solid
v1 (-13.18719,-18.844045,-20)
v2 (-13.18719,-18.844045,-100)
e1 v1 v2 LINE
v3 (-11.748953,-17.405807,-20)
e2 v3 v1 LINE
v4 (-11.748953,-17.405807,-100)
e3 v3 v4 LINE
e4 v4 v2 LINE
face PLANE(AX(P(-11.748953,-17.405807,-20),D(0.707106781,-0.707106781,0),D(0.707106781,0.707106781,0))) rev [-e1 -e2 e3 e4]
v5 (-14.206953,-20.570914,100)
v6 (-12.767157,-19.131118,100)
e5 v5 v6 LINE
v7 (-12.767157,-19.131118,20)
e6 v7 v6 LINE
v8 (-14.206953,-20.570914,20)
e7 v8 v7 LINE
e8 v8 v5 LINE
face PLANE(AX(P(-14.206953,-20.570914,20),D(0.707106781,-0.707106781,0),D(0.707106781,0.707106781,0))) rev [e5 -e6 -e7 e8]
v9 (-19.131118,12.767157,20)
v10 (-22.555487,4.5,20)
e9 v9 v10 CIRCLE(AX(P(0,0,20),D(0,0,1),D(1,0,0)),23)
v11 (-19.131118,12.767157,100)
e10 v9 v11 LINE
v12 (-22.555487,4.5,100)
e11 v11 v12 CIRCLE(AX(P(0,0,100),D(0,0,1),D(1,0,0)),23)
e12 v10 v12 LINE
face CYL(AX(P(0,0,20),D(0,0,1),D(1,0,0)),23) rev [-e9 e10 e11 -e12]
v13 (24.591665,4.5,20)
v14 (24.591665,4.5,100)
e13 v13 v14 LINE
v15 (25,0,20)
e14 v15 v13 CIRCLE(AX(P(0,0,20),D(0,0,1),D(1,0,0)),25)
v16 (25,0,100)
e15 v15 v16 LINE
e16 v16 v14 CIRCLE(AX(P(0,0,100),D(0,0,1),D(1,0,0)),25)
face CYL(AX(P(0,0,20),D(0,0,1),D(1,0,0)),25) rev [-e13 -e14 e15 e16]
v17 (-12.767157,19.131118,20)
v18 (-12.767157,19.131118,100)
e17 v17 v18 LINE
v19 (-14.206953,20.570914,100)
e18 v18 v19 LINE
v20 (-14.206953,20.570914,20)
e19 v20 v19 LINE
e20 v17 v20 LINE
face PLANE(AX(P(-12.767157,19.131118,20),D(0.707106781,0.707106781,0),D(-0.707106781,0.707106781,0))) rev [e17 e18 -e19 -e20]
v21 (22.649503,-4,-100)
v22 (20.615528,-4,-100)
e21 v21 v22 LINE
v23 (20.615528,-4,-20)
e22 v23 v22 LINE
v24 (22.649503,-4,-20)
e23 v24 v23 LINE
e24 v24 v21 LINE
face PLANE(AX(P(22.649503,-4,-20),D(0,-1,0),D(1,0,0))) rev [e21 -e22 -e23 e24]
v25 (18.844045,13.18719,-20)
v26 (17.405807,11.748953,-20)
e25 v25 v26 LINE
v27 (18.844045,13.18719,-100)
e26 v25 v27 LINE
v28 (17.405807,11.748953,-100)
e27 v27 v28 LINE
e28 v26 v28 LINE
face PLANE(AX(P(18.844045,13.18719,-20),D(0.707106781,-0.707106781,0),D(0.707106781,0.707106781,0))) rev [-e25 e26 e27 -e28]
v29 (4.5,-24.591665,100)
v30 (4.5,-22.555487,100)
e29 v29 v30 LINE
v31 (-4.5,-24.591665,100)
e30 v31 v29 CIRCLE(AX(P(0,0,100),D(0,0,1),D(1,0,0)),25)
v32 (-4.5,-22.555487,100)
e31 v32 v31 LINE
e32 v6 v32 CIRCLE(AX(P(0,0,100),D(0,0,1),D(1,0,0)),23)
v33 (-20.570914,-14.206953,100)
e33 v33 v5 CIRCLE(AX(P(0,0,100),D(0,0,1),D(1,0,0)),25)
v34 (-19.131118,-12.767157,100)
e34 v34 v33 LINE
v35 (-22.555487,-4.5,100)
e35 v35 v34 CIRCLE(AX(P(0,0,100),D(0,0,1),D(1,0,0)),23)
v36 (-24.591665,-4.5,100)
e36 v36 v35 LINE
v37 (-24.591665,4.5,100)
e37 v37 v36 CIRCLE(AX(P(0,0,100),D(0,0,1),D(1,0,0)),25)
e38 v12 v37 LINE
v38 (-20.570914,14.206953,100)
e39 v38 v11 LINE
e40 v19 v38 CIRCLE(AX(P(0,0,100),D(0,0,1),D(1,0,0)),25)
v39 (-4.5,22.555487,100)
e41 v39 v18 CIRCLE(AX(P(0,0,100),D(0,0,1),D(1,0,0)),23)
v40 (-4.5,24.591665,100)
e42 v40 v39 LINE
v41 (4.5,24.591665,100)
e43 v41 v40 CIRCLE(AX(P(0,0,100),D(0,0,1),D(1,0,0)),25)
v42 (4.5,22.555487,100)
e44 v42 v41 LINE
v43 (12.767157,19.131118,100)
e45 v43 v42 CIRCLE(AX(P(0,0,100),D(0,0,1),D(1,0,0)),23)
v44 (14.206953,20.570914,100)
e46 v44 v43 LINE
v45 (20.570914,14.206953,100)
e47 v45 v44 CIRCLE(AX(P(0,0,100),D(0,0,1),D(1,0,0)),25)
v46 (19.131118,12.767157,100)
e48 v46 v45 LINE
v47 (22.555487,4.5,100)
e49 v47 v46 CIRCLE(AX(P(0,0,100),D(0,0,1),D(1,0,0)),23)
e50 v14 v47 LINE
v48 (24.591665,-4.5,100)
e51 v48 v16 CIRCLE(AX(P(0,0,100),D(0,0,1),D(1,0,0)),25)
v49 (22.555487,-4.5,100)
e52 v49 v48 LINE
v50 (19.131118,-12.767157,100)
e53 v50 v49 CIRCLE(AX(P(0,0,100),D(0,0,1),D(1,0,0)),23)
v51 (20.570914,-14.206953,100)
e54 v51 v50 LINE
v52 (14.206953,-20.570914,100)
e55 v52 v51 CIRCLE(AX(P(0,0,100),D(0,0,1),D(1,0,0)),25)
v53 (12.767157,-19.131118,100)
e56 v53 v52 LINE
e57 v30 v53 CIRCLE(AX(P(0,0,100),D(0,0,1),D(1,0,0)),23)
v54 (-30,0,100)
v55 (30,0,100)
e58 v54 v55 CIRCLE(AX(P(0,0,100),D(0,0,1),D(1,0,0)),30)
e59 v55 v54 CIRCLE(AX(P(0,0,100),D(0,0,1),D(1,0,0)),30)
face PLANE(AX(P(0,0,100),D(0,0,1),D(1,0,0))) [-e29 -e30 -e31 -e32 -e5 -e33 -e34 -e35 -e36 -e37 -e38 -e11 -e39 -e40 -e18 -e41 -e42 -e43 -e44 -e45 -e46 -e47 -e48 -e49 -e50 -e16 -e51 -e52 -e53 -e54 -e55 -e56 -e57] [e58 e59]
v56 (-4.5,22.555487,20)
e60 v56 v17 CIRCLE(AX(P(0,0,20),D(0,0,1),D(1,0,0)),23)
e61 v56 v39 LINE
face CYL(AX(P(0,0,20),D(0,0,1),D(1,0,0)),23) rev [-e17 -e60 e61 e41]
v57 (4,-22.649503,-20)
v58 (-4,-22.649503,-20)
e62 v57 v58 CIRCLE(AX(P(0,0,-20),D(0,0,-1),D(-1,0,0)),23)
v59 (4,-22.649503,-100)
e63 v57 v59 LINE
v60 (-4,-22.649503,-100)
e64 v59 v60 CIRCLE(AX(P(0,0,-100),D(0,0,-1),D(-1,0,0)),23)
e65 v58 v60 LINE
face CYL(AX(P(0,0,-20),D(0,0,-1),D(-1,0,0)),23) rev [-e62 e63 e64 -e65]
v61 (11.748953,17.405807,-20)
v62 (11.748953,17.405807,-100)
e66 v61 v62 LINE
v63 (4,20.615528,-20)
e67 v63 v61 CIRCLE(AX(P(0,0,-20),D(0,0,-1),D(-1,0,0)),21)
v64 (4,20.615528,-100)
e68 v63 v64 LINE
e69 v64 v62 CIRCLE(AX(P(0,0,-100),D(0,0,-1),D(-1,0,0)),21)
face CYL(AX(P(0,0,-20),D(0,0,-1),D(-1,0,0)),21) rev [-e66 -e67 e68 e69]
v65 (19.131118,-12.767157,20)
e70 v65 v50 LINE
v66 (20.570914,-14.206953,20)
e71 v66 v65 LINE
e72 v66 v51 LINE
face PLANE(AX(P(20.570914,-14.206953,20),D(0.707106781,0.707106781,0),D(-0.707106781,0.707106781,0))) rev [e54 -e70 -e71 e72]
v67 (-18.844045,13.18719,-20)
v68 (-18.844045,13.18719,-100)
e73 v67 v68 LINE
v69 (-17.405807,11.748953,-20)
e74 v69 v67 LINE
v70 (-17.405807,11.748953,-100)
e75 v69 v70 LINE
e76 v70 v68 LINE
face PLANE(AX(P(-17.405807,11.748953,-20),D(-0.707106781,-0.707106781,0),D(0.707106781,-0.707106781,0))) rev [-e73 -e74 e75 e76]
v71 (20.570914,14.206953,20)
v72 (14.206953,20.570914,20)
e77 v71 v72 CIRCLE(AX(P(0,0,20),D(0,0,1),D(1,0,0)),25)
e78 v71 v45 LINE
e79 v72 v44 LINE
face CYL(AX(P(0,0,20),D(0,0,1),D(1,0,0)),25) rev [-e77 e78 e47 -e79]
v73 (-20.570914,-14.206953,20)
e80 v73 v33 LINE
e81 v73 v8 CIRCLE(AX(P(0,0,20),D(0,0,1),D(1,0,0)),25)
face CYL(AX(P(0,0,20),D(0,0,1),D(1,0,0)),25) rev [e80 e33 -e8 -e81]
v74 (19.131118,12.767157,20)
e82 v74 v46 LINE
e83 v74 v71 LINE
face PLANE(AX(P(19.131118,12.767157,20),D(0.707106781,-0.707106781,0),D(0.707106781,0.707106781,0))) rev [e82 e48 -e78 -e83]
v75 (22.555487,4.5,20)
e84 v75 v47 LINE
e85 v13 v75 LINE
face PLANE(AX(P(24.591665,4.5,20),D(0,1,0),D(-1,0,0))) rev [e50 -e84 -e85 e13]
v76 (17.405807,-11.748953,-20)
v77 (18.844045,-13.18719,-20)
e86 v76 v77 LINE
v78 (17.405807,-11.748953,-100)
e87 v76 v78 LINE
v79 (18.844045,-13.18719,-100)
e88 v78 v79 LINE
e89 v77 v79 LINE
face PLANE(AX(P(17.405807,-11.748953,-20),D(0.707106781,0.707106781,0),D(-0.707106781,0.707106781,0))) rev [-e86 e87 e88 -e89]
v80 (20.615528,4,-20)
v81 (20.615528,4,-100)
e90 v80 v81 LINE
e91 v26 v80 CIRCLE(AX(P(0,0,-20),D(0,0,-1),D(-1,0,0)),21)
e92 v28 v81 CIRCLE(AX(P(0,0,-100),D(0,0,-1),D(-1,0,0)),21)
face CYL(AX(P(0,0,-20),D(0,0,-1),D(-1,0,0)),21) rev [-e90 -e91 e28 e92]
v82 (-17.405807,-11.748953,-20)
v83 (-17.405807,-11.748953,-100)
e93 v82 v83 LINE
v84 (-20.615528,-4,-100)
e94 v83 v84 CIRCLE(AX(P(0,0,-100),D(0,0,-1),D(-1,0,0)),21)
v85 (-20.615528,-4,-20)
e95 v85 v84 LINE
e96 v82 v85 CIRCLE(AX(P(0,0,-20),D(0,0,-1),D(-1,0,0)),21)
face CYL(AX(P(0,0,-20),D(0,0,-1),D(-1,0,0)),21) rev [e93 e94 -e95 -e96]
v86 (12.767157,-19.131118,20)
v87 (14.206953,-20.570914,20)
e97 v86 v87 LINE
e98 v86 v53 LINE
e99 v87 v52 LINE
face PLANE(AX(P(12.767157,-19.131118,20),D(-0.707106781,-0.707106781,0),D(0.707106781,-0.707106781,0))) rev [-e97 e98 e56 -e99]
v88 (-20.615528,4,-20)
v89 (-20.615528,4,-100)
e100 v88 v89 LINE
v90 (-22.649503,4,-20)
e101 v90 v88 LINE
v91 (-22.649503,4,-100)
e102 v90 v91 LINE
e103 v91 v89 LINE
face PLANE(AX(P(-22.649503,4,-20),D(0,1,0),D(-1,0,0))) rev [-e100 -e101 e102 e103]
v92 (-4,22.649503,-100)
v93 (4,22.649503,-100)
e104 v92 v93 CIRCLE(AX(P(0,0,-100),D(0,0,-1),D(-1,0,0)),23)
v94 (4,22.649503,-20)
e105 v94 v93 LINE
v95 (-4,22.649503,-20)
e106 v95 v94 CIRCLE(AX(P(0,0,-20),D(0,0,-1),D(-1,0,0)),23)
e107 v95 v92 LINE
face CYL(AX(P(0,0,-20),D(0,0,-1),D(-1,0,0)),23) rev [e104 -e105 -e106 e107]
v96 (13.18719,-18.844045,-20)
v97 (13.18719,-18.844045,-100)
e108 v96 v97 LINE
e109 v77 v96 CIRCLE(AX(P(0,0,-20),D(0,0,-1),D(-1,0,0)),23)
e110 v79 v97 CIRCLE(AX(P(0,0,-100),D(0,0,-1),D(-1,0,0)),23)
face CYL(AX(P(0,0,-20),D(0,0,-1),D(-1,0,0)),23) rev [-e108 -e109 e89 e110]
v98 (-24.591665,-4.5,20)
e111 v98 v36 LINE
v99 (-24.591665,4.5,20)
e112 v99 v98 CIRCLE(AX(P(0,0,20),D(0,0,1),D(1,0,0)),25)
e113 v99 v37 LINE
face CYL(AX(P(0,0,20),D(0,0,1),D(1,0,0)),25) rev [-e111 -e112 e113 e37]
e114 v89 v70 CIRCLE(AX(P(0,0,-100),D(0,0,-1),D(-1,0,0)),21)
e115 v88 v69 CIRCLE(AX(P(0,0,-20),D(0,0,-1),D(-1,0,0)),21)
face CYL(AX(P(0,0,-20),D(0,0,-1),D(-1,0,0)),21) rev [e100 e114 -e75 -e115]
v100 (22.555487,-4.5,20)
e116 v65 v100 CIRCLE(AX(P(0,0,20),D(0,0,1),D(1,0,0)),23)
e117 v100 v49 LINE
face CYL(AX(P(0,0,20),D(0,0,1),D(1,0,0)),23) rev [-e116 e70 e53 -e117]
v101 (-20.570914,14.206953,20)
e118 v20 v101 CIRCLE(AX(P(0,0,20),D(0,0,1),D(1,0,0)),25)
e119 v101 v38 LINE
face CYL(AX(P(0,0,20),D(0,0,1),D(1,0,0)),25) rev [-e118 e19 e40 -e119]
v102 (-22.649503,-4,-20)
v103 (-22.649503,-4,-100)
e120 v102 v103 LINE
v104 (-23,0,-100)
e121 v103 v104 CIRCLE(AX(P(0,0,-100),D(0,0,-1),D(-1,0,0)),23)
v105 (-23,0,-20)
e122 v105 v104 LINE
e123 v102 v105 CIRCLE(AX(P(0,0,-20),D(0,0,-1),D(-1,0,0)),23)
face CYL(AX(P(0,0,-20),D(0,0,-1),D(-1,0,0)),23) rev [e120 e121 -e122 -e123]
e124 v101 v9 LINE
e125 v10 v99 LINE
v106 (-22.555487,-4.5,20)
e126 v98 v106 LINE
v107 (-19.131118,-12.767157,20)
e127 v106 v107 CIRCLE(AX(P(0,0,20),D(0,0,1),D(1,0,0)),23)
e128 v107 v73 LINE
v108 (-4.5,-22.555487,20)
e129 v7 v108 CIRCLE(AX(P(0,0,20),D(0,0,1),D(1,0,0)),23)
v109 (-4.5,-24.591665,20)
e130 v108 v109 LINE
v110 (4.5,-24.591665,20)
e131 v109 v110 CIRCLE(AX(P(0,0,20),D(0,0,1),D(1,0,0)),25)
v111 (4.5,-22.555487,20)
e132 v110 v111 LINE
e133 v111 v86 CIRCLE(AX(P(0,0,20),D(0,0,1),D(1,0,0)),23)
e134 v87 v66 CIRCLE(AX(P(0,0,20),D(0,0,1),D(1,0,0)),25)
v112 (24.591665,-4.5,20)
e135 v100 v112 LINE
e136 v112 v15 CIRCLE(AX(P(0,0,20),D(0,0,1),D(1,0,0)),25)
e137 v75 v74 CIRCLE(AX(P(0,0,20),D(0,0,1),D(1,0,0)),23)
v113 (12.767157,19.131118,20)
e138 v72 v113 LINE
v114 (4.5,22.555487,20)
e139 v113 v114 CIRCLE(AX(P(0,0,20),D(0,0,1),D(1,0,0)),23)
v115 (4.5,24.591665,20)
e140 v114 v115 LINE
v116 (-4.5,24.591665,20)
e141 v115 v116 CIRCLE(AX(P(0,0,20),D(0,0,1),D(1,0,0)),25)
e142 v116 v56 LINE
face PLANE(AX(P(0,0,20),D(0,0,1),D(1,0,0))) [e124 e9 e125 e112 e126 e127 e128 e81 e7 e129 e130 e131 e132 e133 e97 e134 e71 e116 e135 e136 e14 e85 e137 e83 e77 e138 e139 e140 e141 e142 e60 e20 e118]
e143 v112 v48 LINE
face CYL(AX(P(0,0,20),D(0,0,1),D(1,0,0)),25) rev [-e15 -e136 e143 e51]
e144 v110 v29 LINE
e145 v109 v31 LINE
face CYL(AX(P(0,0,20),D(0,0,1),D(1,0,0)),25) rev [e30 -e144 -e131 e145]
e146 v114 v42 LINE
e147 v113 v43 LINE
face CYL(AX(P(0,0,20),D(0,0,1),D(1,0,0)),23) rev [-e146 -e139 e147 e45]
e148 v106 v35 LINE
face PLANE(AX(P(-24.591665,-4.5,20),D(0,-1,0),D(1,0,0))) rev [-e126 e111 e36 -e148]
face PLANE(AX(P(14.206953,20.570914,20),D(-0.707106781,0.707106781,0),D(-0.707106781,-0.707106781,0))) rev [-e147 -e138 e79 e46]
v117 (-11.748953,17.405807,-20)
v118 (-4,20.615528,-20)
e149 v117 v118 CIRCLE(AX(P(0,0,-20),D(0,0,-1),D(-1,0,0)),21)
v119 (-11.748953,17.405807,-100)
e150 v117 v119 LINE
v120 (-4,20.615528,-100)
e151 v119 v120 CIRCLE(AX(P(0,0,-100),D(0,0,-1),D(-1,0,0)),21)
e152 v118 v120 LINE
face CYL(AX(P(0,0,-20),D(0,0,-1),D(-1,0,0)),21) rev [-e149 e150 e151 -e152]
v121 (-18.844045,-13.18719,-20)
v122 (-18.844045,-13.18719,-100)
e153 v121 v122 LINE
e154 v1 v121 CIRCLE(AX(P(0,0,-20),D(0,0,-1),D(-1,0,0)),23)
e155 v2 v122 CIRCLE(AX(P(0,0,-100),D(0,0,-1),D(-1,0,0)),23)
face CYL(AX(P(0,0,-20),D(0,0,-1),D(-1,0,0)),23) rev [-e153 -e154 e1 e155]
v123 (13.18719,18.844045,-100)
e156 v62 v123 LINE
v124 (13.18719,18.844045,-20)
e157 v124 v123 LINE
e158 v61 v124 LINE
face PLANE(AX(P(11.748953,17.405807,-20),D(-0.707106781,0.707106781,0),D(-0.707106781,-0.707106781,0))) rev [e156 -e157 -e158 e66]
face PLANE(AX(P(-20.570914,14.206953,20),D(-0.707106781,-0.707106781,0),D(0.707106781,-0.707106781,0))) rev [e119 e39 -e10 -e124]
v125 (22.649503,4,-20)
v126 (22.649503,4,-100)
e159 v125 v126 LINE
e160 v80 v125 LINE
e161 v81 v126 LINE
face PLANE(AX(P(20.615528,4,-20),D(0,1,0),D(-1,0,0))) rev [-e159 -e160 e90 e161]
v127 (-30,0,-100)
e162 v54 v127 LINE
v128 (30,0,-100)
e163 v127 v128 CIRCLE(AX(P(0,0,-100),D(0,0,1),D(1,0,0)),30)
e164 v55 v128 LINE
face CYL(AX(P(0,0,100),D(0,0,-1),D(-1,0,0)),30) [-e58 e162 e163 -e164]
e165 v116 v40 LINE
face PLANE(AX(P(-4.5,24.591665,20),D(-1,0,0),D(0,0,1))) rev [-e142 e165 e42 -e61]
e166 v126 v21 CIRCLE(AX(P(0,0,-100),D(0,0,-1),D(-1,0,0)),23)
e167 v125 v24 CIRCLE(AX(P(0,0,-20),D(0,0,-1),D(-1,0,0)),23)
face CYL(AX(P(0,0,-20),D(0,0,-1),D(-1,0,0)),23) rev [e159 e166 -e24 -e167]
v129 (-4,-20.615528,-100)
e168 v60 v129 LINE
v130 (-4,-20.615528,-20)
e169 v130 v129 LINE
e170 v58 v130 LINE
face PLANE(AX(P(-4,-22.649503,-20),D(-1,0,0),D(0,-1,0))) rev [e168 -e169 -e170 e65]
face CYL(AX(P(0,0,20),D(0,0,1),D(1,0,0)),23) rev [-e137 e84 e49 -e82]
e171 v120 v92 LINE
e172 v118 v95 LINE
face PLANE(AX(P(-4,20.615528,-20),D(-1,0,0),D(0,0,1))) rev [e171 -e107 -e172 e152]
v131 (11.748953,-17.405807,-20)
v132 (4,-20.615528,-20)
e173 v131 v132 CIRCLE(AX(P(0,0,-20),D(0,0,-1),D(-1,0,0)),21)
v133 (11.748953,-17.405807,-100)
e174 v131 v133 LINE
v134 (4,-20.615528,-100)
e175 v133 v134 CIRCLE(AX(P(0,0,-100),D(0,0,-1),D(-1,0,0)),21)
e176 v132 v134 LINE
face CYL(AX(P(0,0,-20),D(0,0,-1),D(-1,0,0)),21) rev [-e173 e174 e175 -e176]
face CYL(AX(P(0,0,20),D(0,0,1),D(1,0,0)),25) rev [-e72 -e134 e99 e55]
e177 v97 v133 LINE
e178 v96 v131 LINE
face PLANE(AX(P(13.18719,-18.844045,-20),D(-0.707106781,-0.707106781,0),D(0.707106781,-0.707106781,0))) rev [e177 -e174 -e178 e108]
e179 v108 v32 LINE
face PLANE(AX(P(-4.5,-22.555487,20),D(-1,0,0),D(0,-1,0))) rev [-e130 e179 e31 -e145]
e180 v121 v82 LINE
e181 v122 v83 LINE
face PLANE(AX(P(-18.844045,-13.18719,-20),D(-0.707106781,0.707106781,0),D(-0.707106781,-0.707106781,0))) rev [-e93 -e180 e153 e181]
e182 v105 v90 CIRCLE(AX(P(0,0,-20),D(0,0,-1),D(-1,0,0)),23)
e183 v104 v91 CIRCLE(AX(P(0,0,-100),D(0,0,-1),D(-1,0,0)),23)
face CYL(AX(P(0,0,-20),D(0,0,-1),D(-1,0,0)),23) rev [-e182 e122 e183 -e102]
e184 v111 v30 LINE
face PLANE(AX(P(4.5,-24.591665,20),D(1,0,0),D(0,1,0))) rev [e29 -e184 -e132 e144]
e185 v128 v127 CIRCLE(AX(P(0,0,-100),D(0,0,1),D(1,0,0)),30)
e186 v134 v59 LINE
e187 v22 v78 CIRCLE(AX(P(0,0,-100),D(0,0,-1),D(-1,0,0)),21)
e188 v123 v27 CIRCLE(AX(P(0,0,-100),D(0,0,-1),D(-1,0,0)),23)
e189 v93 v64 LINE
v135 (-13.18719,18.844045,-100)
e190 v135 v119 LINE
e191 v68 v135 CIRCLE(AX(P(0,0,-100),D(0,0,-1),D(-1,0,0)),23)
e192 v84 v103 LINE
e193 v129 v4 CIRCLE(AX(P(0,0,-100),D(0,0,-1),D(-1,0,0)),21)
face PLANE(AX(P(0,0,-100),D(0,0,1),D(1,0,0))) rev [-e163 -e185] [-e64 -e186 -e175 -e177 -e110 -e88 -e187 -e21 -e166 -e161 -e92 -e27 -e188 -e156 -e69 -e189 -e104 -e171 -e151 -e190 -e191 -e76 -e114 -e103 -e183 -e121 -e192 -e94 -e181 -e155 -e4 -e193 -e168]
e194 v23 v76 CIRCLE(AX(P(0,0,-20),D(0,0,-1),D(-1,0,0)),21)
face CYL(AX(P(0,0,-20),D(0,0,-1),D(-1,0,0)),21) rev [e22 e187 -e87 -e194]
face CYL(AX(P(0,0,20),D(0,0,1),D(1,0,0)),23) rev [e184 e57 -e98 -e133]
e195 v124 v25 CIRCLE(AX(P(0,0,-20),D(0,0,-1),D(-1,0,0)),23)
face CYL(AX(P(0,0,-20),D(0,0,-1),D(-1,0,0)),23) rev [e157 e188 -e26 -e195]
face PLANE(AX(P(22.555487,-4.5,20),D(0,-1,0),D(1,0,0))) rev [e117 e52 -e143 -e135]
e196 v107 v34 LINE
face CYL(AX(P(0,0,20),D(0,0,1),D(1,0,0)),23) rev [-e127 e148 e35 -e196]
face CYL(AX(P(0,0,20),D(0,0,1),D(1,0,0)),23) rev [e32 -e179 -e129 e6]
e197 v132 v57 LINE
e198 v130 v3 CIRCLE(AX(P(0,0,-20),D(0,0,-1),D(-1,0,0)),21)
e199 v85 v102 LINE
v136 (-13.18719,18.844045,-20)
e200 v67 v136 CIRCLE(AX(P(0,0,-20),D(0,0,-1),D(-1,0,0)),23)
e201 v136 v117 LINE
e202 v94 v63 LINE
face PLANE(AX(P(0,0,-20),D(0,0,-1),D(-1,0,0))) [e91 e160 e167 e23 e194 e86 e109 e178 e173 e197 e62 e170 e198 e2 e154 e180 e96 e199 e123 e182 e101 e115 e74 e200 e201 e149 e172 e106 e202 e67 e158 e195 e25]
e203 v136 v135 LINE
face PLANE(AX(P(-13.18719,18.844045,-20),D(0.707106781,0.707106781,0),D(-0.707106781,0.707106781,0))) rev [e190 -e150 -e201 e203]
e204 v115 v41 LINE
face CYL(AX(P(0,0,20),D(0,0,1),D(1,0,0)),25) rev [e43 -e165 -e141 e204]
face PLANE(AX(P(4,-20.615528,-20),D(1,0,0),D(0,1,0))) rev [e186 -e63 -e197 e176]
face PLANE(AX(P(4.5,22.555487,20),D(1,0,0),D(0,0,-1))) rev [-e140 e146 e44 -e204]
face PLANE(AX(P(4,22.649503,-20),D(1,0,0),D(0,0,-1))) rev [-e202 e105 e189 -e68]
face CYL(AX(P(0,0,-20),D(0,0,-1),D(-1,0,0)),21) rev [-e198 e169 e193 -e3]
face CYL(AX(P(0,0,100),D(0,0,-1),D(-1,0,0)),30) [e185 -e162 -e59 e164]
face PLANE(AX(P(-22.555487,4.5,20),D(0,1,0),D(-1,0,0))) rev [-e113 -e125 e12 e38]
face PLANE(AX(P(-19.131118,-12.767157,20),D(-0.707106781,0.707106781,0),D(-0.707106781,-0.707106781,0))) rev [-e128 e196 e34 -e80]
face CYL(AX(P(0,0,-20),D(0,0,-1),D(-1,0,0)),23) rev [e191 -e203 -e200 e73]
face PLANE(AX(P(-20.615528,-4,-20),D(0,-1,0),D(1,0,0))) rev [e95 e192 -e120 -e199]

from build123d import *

# Parameters (mm, degrees)
SKETCH_1_R          = 30
EXTRUDE_1_DEPTH     = 100
CUT_EXTRUDE_1_DEPTH = 80
CUT_EXTRUDE_START   = -80
CUT_EXTRUDE_2_DEPTH = 80


with BuildPart() as part:
    # 草图1 → 凸台-拉伸1 (new, symmetric)
    with BuildSketch(Plane.XY):
        with Locations(Location((0, 0, 0), (0, 0, 180))):
            Circle(SKETCH_1_R)
    extrude(amount=EXTRUDE_1_DEPTH, both=True)

    # 草图2 → 切除-拉伸1 (cut)
    with BuildSketch(Plane.XY.offset(100)):
        with BuildLine():
            Line((-4.5, 24.591665255), (-4.5, 22.555487137))
            ThreePointArc((-4.5, 22.555487137), (-8.801718944, 21.249229248), (-12.767157392, 19.131118423))
            Line((-12.767157392, 19.131118423), (-14.206952747, 20.570913778))
            ThreePointArc((-14.206952747, 20.570913778), (-17.67766953, 17.67766953), (-20.570913778, 14.206952747))
            Line((-20.570913778, 14.206952747), (-19.131118423, 12.767157392))
            ThreePointArc((-19.131118423, 12.767157392), (-21.249229248, 8.801718944), (-22.555487137, 4.5))
            Line((-22.555487137, 4.5), (-24.591665255, 4.5))
            ThreePointArc((-24.591665255, 4.5), (-25, 0), (-24.591665255, -4.5))
            Line((-24.591665255, -4.5), (-22.555487137, -4.5))
            ThreePointArc((-22.555487137, -4.5), (-21.249229248, -8.801718944), (-19.131118423, -12.767157392))
            Line((-19.131118423, -12.767157392), (-20.570913778, -14.206952747))
            ThreePointArc((-20.570913778, -14.206952747), (-17.67766953, -17.67766953), (-14.206952747, -20.570913778))
            Line((-14.206952747, -20.570913778), (-12.767157392, -19.131118423))
            ThreePointArc((-12.767157392, -19.131118423), (-8.801718944, -21.249229248), (-4.5, -22.555487137))
            Line((-4.5, -22.555487137), (-4.5, -24.591665255))
            ThreePointArc((-4.5, -24.591665255), (0, -25), (4.5, -24.591665255))
            Line((4.5, -24.591665255), (4.5, -22.555487137))
            ThreePointArc((4.5, -22.555487137), (8.801718944, -21.249229248), (12.767157392, -19.131118423))
            Line((12.767157392, -19.131118423), (14.206952747, -20.570913778))
            ThreePointArc((14.206952747, -20.570913778), (17.67766953, -17.67766953), (20.570913778, -14.206952747))
            Line((20.570913778, -14.206952747), (19.131118423, -12.767157392))
            ThreePointArc((19.131118423, -12.767157392), (21.249229248, -8.801718944), (22.555487137, -4.5))
            Line((22.555487137, -4.5), (24.591665255, -4.5))
            ThreePointArc((24.591665255, -4.5), (25, 0), (24.591665255, 4.5))
            Line((24.591665255, 4.5), (22.555487137, 4.5))
            ThreePointArc((22.555487137, 4.5), (21.249229248, 8.801718944), (19.131118423, 12.767157392))
            Line((19.131118423, 12.767157392), (20.570913778, 14.206952747))
            ThreePointArc((20.570913778, 14.206952747), (17.67766953, 17.67766953), (14.206952747, 20.570913778))
            Line((14.206952747, 20.570913778), (12.767157392, 19.131118423))
            ThreePointArc((12.767157392, 19.131118423), (8.801718944, 21.249229248), (4.5, 22.555487137))
            Line((4.5, 22.555487137), (4.5, 24.591665255))
            ThreePointArc((4.5, 24.591665255), (0, 25), (-4.5, 24.591665255))
        make_face()
    extrude(amount=-CUT_EXTRUDE_1_DEPTH, mode=Mode.SUBTRACT)

    # 草图3 → 切除-拉伸2 (cut)
    with BuildSketch(Plane(origin=(0, 0, -100), x_dir=(-1, 0, 0), z_dir=(0, 0, -1)).offset(CUT_EXTRUDE_START)):
        with BuildLine():
            Line((-4, 22.649503306), (-4, 20.615528128))
            ThreePointArc((-4, 20.615528128), (-8.03635208, 19.401470183), (-11.748952612, 17.405806862))
            Line((-11.748952612, 17.405806862), (-13.187190253, 18.844044503))
            ThreePointArc((-13.187190253, 18.844044503), (-16.263455967, 16.263455967), (-18.844044503, 13.187190253))
            Line((-18.844044503, 13.187190253), (-17.405806862, 11.748952612))
            ThreePointArc((-17.405806862, 11.748952612), (-19.401470183, 8.03635208), (-20.615528128, 4))
            Line((-20.615528128, 4), (-22.649503306, 4))
            ThreePointArc((-22.649503306, 4), (-23, 0), (-22.649503306, -4))
            Line((-22.649503306, -4), (-20.615528128, -4))
            ThreePointArc((-20.615528128, -4), (-19.401470183, -8.03635208), (-17.405806862, -11.748952612))
            Line((-17.405806862, -11.748952612), (-18.844044503, -13.187190253))
            ThreePointArc((-18.844044503, -13.187190253), (-16.263455967, -16.263455967), (-13.187190253, -18.844044503))
            Line((-13.187190253, -18.844044503), (-11.748952612, -17.405806862))
            ThreePointArc((-11.748952612, -17.405806862), (-8.03635208, -19.401470183), (-4, -20.615528128))
            Line((-4, -20.615528128), (-4, -22.649503306))
            ThreePointArc((-4, -22.649503306), (0, -23), (4, -22.649503306))
            Line((4, -22.649503306), (4, -20.615528128))
            ThreePointArc((4, -20.615528128), (8.03635208, -19.401470183), (11.748952612, -17.405806862))
            Line((11.748952612, -17.405806862), (13.187190253, -18.844044503))
            ThreePointArc((13.187190253, -18.844044503), (16.263455967, -16.263455967), (18.844044503, -13.187190253))
            Line((18.844044503, -13.187190253), (17.405806862, -11.748952612))
            ThreePointArc((17.405806862, -11.748952612), (19.401470183, -8.03635208), (20.615528128, -4))
            Line((20.615528128, -4), (22.649503306, -4))
            ThreePointArc((22.649503306, -4), (23, 0), (22.649503306, 4))
            Line((22.649503306, 4), (20.615528128, 4))
            ThreePointArc((20.615528128, 4), (19.401470183, 8.03635208), (17.405806862, 11.748952612))
            Line((17.405806862, 11.748952612), (18.844044503, 13.187190253))
            ThreePointArc((18.844044503, 13.187190253), (16.263455967, 16.263455967), (13.187190253, 18.844044503))
            Line((13.187190253, 18.844044503), (11.748952612, 17.405806862))
            ThreePointArc((11.748952612, 17.405806862), (8.03635208, 19.401470183), (4, 20.615528128))
            Line((4, 20.615528128), (4, 22.649503306))
            ThreePointArc((4, 22.649503306), (0, 23), (-4, 22.649503306))
        make_face()
    extrude(amount=CUT_EXTRUDE_2_DEPTH, mode=Mode.SUBTRACT)


solid = part.part
